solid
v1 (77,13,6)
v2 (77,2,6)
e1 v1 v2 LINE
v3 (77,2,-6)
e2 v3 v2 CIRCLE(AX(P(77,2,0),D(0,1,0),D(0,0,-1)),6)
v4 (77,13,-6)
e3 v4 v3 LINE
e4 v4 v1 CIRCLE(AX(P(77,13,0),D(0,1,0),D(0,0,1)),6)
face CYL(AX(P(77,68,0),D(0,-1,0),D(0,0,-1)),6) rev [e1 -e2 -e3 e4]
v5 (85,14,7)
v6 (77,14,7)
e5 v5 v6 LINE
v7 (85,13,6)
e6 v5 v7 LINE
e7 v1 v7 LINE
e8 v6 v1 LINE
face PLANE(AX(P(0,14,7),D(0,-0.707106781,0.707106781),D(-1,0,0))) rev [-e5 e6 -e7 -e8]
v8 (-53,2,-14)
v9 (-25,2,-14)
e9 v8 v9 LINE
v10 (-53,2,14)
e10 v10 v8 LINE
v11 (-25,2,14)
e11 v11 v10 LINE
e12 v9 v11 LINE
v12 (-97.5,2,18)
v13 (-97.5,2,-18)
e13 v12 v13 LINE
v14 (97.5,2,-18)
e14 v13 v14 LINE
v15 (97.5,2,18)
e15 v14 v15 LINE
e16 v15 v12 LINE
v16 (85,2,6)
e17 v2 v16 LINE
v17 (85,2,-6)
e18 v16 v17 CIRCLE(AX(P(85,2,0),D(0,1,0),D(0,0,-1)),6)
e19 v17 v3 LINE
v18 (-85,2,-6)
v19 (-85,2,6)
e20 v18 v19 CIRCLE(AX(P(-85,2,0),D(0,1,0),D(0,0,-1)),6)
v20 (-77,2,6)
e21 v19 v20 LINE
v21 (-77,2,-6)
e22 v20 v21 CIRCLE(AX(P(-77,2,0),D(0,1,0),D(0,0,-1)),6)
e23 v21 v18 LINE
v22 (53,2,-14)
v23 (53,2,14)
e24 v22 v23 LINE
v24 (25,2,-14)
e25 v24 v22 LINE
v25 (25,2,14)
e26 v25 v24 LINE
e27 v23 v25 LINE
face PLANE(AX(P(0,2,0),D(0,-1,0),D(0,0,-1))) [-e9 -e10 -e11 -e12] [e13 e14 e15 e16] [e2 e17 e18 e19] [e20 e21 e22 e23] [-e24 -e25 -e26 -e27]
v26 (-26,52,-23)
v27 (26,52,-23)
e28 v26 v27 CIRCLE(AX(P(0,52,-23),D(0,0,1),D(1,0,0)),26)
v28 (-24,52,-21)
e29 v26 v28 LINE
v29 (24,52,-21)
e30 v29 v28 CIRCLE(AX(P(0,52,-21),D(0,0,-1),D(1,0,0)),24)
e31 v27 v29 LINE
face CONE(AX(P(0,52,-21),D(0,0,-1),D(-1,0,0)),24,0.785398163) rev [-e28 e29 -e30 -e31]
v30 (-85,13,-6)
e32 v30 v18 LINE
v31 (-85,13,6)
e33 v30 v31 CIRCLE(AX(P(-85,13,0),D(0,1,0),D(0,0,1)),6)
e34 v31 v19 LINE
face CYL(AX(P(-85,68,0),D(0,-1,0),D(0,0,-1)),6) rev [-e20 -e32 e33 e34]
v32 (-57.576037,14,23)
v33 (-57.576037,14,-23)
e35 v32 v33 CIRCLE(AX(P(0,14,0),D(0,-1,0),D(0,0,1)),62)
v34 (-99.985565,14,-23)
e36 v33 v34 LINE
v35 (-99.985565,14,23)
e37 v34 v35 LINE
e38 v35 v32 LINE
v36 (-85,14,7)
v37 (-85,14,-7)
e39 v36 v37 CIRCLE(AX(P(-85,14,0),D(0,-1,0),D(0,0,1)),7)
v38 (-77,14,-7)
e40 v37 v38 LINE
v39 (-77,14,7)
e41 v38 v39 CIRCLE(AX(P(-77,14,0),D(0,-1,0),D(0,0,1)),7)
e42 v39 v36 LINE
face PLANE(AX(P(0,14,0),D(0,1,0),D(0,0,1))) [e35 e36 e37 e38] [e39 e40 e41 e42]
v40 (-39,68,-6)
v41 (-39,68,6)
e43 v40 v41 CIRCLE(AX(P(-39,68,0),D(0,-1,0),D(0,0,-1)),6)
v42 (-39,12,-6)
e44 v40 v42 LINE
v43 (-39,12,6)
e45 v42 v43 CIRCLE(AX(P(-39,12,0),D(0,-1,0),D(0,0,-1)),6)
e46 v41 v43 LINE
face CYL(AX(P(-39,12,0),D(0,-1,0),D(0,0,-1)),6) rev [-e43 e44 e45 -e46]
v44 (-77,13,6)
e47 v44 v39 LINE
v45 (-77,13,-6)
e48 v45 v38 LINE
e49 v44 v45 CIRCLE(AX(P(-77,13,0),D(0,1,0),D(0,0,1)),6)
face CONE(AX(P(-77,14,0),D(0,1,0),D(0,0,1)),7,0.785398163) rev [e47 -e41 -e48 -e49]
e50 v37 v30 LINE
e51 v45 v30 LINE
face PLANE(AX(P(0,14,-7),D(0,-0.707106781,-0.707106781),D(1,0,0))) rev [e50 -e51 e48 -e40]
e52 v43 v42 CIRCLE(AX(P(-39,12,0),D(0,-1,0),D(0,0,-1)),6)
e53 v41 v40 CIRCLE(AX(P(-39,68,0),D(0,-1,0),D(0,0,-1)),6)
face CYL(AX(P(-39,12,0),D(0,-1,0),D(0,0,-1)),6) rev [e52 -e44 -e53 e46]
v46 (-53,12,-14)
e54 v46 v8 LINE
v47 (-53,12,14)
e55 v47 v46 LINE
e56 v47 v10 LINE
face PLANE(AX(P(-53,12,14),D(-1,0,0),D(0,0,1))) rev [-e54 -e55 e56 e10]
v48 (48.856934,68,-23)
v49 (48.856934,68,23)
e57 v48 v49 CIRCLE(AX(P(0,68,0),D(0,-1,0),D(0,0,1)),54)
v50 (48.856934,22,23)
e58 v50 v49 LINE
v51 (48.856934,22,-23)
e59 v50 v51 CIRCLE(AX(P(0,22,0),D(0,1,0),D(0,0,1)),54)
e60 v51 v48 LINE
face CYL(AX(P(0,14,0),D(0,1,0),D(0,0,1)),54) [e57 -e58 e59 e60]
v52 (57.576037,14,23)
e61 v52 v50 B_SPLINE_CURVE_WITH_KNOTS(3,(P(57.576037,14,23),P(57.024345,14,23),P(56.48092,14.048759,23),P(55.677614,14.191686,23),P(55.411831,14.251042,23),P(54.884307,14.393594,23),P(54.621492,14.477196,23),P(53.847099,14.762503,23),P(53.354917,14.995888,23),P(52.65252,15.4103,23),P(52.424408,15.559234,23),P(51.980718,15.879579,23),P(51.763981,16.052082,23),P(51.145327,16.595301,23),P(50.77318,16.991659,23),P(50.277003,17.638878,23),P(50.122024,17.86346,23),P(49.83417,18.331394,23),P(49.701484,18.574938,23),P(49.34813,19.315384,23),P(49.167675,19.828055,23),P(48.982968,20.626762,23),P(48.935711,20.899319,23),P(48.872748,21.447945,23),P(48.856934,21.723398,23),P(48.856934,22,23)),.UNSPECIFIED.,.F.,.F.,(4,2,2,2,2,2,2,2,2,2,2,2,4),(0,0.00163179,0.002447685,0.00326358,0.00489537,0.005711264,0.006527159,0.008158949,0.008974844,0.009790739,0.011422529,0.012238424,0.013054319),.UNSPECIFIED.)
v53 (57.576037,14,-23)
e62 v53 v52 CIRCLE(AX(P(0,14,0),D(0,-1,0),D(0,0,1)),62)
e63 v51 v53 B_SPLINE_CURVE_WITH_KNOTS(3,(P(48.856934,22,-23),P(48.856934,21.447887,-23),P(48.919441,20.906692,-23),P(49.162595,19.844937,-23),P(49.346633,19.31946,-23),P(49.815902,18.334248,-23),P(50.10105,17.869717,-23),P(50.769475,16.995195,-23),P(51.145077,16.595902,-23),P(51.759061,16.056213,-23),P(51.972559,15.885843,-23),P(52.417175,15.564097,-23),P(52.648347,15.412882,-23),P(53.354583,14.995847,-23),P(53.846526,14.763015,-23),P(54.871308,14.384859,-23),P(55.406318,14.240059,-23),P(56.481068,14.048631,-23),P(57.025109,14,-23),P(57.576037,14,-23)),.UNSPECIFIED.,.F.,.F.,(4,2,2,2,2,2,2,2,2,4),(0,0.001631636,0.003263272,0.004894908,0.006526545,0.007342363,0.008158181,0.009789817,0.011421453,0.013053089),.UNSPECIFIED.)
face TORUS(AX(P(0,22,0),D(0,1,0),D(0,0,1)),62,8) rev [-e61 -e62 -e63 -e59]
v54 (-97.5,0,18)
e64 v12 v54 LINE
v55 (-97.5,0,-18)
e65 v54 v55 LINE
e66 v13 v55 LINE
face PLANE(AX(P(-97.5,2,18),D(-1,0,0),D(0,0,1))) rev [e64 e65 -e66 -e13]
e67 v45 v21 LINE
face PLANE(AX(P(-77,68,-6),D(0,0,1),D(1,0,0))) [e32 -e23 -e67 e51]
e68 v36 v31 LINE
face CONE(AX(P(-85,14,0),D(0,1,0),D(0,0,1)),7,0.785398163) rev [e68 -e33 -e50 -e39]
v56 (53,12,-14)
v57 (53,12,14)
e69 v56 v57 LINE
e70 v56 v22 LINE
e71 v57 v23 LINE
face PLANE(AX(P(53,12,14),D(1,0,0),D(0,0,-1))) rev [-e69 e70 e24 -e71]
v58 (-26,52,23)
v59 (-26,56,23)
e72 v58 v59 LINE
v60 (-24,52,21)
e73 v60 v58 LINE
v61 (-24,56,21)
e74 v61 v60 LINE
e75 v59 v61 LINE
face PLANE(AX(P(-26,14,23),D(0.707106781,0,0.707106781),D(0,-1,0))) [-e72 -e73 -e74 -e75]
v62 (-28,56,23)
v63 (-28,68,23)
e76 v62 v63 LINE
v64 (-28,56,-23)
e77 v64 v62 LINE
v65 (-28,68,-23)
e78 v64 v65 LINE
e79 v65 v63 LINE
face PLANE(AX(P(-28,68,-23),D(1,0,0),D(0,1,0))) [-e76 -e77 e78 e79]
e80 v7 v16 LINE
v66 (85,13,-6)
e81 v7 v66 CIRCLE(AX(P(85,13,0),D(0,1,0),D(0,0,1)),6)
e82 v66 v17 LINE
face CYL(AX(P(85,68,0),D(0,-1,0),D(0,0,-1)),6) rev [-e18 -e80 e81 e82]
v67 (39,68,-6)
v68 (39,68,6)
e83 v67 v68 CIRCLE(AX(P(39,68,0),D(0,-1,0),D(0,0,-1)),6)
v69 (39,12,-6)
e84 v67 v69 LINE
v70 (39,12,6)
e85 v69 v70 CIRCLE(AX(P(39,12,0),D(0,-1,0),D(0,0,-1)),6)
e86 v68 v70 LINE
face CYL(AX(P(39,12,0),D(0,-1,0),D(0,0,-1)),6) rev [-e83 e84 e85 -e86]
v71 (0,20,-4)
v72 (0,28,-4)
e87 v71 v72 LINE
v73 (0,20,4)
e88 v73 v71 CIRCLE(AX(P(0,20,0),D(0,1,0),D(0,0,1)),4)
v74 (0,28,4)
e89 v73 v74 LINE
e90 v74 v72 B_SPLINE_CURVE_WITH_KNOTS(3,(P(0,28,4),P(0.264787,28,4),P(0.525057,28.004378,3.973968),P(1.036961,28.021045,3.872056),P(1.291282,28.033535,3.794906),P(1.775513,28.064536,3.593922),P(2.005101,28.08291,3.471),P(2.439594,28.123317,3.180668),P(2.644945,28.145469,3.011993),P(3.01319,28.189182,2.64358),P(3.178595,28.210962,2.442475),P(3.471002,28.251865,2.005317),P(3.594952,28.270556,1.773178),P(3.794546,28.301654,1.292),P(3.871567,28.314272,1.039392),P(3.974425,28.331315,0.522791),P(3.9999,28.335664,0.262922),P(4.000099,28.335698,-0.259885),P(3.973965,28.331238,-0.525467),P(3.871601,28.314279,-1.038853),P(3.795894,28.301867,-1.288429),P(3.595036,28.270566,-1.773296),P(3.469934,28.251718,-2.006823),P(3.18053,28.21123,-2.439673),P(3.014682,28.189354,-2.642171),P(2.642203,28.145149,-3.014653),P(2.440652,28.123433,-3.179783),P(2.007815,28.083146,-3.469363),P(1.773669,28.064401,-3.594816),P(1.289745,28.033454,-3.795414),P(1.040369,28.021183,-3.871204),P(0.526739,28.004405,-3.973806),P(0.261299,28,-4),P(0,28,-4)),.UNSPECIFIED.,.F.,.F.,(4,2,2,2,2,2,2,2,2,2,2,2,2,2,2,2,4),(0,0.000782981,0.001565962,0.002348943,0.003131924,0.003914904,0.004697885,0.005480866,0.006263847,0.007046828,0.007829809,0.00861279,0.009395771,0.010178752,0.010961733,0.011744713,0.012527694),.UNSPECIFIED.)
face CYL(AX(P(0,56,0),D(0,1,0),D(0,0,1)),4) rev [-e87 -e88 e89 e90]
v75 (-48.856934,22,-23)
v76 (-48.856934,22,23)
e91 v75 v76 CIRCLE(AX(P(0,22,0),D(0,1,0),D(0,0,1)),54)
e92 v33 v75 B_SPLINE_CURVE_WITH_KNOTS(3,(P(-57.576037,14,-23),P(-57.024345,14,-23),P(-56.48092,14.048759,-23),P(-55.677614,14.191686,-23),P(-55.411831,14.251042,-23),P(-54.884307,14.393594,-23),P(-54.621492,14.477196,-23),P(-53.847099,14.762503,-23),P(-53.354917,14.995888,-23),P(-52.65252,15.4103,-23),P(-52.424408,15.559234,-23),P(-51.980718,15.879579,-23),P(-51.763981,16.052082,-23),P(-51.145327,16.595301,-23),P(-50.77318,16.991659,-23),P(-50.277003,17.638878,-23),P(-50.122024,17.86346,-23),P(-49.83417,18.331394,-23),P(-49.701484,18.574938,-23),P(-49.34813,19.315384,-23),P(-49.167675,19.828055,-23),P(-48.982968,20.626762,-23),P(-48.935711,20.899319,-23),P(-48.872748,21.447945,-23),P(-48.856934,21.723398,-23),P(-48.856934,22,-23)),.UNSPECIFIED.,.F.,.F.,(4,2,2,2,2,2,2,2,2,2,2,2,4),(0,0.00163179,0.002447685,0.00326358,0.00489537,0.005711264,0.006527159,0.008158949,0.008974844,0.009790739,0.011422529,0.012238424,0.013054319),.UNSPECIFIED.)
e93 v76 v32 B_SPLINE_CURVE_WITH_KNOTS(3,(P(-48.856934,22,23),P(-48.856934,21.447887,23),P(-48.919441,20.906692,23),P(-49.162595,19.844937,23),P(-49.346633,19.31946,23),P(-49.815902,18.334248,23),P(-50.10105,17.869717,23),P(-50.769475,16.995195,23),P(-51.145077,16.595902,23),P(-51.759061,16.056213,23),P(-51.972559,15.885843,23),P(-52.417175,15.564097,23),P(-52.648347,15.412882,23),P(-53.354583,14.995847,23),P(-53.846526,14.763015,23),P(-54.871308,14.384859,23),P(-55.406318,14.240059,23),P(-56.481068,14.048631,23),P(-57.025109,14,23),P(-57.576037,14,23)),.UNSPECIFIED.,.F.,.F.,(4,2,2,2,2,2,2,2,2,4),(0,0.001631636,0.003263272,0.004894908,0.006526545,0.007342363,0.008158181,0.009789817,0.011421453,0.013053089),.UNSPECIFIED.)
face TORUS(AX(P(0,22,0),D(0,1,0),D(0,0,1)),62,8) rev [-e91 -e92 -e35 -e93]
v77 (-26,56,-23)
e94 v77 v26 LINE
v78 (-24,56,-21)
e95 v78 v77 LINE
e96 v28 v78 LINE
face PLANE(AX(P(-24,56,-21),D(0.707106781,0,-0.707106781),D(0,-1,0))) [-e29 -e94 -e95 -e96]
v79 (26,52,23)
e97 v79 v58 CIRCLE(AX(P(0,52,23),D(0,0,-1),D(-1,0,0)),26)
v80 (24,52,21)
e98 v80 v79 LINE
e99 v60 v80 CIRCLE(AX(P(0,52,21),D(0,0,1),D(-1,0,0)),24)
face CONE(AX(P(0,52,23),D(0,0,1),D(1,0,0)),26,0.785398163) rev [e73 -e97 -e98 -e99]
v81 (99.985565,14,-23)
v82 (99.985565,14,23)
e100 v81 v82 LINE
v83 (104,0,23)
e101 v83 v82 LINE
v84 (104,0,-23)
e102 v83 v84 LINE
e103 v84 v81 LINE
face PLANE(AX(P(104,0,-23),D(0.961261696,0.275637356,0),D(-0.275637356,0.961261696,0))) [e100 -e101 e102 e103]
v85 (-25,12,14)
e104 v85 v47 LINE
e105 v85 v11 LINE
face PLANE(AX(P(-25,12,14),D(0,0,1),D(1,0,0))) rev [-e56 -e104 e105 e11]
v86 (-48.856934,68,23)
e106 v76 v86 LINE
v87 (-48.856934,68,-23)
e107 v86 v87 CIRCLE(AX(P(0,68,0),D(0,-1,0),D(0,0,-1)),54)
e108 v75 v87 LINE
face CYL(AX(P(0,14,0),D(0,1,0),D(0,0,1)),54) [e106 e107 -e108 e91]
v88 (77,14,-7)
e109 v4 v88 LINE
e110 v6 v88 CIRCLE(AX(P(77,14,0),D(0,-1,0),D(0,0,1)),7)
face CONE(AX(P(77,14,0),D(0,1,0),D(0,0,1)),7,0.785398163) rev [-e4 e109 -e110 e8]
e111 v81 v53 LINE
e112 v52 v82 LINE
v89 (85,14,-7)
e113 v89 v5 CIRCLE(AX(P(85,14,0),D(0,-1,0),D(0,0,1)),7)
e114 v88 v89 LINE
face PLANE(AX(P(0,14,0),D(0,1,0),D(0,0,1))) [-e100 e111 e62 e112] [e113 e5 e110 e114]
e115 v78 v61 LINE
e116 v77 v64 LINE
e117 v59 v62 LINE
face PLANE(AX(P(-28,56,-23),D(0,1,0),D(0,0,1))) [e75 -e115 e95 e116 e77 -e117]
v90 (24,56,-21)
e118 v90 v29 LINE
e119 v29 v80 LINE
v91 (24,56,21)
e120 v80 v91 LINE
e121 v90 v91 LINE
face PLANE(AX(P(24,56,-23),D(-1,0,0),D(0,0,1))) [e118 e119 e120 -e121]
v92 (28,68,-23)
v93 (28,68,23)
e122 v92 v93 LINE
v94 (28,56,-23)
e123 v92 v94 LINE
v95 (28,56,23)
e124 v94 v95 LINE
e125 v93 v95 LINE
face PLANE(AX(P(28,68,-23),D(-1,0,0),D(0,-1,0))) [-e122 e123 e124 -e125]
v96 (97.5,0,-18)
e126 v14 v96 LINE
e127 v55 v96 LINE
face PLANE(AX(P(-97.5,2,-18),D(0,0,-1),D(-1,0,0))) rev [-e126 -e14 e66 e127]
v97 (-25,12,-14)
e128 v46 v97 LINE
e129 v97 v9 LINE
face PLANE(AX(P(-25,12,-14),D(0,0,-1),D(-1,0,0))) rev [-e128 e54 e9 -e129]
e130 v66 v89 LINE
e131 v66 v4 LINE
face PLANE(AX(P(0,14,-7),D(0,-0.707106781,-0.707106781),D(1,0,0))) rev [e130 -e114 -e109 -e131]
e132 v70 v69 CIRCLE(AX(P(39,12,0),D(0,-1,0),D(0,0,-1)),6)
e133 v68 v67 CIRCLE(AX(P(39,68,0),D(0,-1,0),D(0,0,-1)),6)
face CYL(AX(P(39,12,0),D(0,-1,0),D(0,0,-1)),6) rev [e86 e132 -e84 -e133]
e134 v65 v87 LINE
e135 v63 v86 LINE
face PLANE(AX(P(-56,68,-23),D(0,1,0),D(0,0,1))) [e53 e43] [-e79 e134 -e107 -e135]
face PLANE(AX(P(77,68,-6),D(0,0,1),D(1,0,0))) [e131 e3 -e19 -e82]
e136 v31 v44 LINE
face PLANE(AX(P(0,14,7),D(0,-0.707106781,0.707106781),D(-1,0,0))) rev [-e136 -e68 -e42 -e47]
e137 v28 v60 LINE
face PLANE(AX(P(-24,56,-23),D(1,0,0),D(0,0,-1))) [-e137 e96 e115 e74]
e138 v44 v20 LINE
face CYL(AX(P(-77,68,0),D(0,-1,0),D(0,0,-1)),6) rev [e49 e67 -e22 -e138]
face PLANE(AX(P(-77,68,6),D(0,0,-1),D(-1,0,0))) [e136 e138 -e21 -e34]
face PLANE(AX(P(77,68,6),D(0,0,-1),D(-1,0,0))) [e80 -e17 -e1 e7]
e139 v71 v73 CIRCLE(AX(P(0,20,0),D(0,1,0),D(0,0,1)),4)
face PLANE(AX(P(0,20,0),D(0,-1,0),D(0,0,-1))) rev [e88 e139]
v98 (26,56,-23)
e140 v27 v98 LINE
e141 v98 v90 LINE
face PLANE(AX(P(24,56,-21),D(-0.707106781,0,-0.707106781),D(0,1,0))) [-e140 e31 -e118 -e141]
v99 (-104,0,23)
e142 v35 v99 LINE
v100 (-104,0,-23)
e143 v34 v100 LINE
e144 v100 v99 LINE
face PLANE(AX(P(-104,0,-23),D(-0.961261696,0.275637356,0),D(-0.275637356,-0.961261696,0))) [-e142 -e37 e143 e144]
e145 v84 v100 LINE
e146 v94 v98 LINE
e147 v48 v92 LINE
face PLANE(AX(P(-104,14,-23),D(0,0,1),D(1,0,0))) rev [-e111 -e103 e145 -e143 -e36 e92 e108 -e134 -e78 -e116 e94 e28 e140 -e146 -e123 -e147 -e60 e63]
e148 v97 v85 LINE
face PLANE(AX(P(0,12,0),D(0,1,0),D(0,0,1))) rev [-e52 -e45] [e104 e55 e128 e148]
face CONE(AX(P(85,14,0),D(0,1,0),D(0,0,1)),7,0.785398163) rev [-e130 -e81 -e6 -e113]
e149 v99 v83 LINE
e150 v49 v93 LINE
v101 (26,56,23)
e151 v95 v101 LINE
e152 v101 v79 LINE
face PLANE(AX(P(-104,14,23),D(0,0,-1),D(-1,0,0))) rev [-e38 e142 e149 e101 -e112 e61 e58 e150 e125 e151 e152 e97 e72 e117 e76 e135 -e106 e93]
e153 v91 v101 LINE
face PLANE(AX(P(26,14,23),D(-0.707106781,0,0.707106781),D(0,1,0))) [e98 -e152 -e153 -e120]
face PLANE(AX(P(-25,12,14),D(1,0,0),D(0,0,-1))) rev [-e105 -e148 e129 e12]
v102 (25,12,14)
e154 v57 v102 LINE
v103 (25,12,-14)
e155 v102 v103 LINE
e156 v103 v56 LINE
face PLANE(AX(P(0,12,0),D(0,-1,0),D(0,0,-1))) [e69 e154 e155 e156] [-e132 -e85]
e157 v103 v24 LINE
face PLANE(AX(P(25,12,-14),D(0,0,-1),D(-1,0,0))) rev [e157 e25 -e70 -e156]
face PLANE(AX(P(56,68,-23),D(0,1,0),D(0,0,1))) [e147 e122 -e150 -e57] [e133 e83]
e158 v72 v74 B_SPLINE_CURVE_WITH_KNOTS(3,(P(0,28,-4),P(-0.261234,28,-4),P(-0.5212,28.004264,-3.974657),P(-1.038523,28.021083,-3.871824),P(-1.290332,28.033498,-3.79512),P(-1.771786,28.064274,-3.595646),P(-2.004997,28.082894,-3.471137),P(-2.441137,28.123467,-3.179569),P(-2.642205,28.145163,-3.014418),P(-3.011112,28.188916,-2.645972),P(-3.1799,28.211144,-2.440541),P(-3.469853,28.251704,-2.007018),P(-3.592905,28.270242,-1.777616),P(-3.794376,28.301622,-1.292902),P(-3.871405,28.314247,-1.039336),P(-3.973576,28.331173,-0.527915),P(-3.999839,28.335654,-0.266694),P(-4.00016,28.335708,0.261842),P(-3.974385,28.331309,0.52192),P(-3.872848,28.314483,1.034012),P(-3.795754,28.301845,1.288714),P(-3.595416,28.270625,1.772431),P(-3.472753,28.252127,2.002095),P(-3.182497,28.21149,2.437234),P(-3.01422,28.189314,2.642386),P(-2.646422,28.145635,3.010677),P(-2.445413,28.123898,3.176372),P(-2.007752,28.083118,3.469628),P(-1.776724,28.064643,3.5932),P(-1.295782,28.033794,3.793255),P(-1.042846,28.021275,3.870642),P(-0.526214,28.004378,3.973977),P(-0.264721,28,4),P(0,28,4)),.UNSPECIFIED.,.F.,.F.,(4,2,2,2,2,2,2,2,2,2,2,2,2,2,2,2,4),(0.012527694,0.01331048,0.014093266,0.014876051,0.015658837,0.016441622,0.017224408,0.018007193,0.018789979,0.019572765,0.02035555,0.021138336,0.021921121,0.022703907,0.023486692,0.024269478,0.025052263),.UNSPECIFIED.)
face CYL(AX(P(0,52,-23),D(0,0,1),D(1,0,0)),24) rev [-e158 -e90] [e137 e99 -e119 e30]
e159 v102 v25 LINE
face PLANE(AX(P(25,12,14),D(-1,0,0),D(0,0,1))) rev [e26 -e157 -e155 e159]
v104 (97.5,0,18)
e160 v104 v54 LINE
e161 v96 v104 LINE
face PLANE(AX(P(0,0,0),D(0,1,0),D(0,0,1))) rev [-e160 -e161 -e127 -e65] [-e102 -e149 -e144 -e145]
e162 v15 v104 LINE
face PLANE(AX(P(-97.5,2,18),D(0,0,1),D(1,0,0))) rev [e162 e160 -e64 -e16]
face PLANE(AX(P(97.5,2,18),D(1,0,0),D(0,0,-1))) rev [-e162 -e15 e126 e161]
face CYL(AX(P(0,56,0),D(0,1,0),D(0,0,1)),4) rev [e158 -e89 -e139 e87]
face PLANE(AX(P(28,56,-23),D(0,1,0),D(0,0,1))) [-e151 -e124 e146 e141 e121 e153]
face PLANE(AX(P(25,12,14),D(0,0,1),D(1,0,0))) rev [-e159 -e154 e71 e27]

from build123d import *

# Parameters (mm, degrees)
BASE_PLATE_SKETCH_W             = 208
BASE_PLATE_SKETCH_H             = 46
BASE_PLATE_208X46X14_DEPTH      = 14
BASE_END_BEVEL_SKETCH_OUTSIDE_W = 252.698
BASE_END_BEVEL_SKETCH_OUTSIDE_H = 58.698
BASE_END_BEVELS_DEPTH           = 115.577484699
BEARING_PEDESTAL_DEPTH          = 46
UNDERSIDE_RELIEF_SKETCH_W       = 195
UNDERSIDE_RELIEF_SKETCH_H       = 36
UNDERSIDE_RELIEF_2MM_DEPTH      = 2
BEARING_BORE_SKETCH_W           = 28
BEARING_BORE_SKETCH_H           = 28
BEARING_BORE_CUT_DEPTH          = 10
MOUNTING_SLOTS_2X8_DEPTH        = 127.368508735
CAP_BOLT_HOLES_2X_12_D          = 12
PEDESTAL_CHAMFER_2MM_SIZE       = 2
SLOT_EDGE_CHAMFER_1MM_SIZE      = 1
DRILLED_HOLE_8_D                = 8
DRILLED_HOLE_8_DEPTH            = 36
PEDESTAL_PROFILE_CUT_DEPTH      = 54
PEDESTAL_BASE_FILLET_R8_R       = 8


with BuildPart() as part:
    # Base Plate Sketch → Base Plate 208x46x14 (new body)
    with BuildSketch(Plane(origin=(0, 0, 0), x_dir=(1, 0, 0), z_dir=(0, 1, 0))):
        Rectangle(BASE_PLATE_SKETCH_W, BASE_PLATE_SKETCH_H)
    extrude(amount=BASE_PLATE_208X46X14_DEPTH)

    # Base End Bevel Sketch outside → Base End Bevels (cut, through all)
    with BuildSketch(Plane.XY.offset(23)):
        with Locations((0, 7)):
            Rectangle(BASE_END_BEVEL_SKETCH_OUTSIDE_W, BASE_END_BEVEL_SKETCH_OUTSIDE_H)
        Polygon((-104, 0), (-99.985564599, 14), (99.985564599, 14), (104, 0), align=None, mode=Mode.SUBTRACT)
    extrude(amount=-BASE_END_BEVELS_DEPTH, mode=Mode.SUBTRACT)

    # Pedestal Sketch → Bearing Pedestal (add, through all)
    with BuildSketch(Plane.XY.offset(23)):
        with BuildLine():
            Line((-56, 14), (56, 14))
            Line((56, 14), (56, 68))
            Line((56, 68), (28, 68))
            Line((28, 68), (28, 56))
            Line((28, 56), (24, 56))
            Line((24, 56), (24, 52))
            ThreePointArc((24, 52), (0, 28), (-24, 52))
            Line((-24, 52), (-24, 56))
            Line((-24, 56), (-28, 56))
            Line((-28, 56), (-28, 68))
            Line((-28, 68), (-56, 68))
            Line((-56, 68), (-56, 14))
        make_face()
    extrude(amount=-BEARING_PEDESTAL_DEPTH)

    # Underside Relief Sketch → Underside Relief 2mm (cut)
    with BuildSketch(Plane.XZ):
        Rectangle(UNDERSIDE_RELIEF_SKETCH_W, UNDERSIDE_RELIEF_SKETCH_H)
    extrude(amount=-UNDERSIDE_RELIEF_2MM_DEPTH, mode=Mode.SUBTRACT)

    # Bearing Bore Sketch → Bearing Bore Cut (cut)
    with BuildSketch(Plane.XZ.offset(-2)):
        with Locations((39, 0)):
            Rectangle(BEARING_BORE_SKETCH_W, BEARING_BORE_SKETCH_H)
        with Locations((-39, 0)):
            Rectangle(BEARING_BORE_SKETCH_W, BEARING_BORE_SKETCH_H)
    extrude(amount=-BEARING_BORE_CUT_DEPTH, mode=Mode.SUBTRACT)

    # Mounting Slots Sketch → Mounting Slots 2x8 (cut, through all)
    with BuildSketch(Plane(origin=(0, 0, 0), x_dir=(1, 0, 0), z_dir=(0, 1, 0))):
        with BuildLine():
            Line((77, 6), (85, 6))
            ThreePointArc((85, 6), (91, 0), (85, -6))
            Line((85, -6), (77, -6))
            ThreePointArc((77, -6), (71, 0), (77, 6))
        make_face()
        with BuildLine():
            Line((-77, 6), (-85, 6))
            ThreePointArc((-85, 6), (-91, 0), (-85, -6))
            Line((-85, -6), (-77, -6))
            ThreePointArc((-77, -6), (-71, 0), (-77, 6))
        make_face()
    extrude(amount=MOUNTING_SLOTS_2X8_DEPTH, mode=Mode.SUBTRACT)

    # Cap Bolt Holes 2xØ12 (through all)
    with Locations(Plane(origin=(0, 12, 0), x_dir=(-1, 0, 0), z_dir=(0, -1, 0))):
        with Locations((-39, 0), (39, 0)):
            Hole(CAP_BOLT_HOLES_2X_12_D / 2)

    # Pedestal Chamfer 2mm
    pedestal_chamfer_2mm_edges = [part.edges().sort_by_distance(p)[0] for p in [
        (-24, 54, -23),
        (0, 28, -23),
        (24, 54, -23),
        (24, 54, 23),
        (0, 28, 23),
        (-24, 54, 23),
    ]]
    chamfer(pedestal_chamfer_2mm_edges, length=PEDESTAL_CHAMFER_2MM_SIZE)

    # Slot Edge Chamfer 1mm
    slot_edge_chamfer_1mm_edges = [part.edges().sort_by_distance(p)[0] for p in [
        (71, 14, 0),
        (81, 14, 6),
        (91, 14, 0),
        (81, 14, -6),
        (-71, 14, 0),
        (-81, 14, -6),
        (-91, 14, 0),
        (-81, 14, 6),
    ]]
    chamfer(slot_edge_chamfer_1mm_edges, length=SLOT_EDGE_CHAMFER_1MM_SIZE)

    # Drilled Hole Ø8
    with Locations(Plane(origin=(0, 56, 0), x_dir=(1, 0, 0), z_dir=(0, 1, 0))):
        with Locations((0, 0)):
            Hole(DRILLED_HOLE_8_D / 2, depth=DRILLED_HOLE_8_DEPTH)

    # Pedestal Profile Sketch → Pedestal Profile Cut (cut)
    with BuildSketch(Plane(origin=(0, 68, 0), x_dir=(1, 0, 0), z_dir=(0, 1, 0))):
        with BuildLine():
            Line((-56, -23), (-48.856934001, -23))
            ThreePointArc((-48.856934001, -23), (-54, 0), (-48.856934001, 23))
            Line((-48.856934001, 23), (-56, 23))
            Line((-56, 23), (-56, -23))
        make_face()
        with BuildLine():
            Line((48.856934001, -23), (56, -23))
            Line((56, -23), (56, 23))
            Line((56, 23), (48.856934001, 23))
            ThreePointArc((48.856934001, 23), (54, 0), (48.856934001, -23))
        make_face()
    extrude(amount=-PEDESTAL_PROFILE_CUT_DEPTH, mode=Mode.SUBTRACT)

    # Pedestal Base Fillet R8
    pedestal_base_fillet_r8_edges = [part.edges().sort_by_distance(p)[0] for p in [
        (-54, 14, 0),
        (54, 14, 0),
    ]]
    fillet(pedestal_base_fillet_r8_edges, radius=PEDESTAL_BASE_FILLET_R8_R)


solid = part.part
